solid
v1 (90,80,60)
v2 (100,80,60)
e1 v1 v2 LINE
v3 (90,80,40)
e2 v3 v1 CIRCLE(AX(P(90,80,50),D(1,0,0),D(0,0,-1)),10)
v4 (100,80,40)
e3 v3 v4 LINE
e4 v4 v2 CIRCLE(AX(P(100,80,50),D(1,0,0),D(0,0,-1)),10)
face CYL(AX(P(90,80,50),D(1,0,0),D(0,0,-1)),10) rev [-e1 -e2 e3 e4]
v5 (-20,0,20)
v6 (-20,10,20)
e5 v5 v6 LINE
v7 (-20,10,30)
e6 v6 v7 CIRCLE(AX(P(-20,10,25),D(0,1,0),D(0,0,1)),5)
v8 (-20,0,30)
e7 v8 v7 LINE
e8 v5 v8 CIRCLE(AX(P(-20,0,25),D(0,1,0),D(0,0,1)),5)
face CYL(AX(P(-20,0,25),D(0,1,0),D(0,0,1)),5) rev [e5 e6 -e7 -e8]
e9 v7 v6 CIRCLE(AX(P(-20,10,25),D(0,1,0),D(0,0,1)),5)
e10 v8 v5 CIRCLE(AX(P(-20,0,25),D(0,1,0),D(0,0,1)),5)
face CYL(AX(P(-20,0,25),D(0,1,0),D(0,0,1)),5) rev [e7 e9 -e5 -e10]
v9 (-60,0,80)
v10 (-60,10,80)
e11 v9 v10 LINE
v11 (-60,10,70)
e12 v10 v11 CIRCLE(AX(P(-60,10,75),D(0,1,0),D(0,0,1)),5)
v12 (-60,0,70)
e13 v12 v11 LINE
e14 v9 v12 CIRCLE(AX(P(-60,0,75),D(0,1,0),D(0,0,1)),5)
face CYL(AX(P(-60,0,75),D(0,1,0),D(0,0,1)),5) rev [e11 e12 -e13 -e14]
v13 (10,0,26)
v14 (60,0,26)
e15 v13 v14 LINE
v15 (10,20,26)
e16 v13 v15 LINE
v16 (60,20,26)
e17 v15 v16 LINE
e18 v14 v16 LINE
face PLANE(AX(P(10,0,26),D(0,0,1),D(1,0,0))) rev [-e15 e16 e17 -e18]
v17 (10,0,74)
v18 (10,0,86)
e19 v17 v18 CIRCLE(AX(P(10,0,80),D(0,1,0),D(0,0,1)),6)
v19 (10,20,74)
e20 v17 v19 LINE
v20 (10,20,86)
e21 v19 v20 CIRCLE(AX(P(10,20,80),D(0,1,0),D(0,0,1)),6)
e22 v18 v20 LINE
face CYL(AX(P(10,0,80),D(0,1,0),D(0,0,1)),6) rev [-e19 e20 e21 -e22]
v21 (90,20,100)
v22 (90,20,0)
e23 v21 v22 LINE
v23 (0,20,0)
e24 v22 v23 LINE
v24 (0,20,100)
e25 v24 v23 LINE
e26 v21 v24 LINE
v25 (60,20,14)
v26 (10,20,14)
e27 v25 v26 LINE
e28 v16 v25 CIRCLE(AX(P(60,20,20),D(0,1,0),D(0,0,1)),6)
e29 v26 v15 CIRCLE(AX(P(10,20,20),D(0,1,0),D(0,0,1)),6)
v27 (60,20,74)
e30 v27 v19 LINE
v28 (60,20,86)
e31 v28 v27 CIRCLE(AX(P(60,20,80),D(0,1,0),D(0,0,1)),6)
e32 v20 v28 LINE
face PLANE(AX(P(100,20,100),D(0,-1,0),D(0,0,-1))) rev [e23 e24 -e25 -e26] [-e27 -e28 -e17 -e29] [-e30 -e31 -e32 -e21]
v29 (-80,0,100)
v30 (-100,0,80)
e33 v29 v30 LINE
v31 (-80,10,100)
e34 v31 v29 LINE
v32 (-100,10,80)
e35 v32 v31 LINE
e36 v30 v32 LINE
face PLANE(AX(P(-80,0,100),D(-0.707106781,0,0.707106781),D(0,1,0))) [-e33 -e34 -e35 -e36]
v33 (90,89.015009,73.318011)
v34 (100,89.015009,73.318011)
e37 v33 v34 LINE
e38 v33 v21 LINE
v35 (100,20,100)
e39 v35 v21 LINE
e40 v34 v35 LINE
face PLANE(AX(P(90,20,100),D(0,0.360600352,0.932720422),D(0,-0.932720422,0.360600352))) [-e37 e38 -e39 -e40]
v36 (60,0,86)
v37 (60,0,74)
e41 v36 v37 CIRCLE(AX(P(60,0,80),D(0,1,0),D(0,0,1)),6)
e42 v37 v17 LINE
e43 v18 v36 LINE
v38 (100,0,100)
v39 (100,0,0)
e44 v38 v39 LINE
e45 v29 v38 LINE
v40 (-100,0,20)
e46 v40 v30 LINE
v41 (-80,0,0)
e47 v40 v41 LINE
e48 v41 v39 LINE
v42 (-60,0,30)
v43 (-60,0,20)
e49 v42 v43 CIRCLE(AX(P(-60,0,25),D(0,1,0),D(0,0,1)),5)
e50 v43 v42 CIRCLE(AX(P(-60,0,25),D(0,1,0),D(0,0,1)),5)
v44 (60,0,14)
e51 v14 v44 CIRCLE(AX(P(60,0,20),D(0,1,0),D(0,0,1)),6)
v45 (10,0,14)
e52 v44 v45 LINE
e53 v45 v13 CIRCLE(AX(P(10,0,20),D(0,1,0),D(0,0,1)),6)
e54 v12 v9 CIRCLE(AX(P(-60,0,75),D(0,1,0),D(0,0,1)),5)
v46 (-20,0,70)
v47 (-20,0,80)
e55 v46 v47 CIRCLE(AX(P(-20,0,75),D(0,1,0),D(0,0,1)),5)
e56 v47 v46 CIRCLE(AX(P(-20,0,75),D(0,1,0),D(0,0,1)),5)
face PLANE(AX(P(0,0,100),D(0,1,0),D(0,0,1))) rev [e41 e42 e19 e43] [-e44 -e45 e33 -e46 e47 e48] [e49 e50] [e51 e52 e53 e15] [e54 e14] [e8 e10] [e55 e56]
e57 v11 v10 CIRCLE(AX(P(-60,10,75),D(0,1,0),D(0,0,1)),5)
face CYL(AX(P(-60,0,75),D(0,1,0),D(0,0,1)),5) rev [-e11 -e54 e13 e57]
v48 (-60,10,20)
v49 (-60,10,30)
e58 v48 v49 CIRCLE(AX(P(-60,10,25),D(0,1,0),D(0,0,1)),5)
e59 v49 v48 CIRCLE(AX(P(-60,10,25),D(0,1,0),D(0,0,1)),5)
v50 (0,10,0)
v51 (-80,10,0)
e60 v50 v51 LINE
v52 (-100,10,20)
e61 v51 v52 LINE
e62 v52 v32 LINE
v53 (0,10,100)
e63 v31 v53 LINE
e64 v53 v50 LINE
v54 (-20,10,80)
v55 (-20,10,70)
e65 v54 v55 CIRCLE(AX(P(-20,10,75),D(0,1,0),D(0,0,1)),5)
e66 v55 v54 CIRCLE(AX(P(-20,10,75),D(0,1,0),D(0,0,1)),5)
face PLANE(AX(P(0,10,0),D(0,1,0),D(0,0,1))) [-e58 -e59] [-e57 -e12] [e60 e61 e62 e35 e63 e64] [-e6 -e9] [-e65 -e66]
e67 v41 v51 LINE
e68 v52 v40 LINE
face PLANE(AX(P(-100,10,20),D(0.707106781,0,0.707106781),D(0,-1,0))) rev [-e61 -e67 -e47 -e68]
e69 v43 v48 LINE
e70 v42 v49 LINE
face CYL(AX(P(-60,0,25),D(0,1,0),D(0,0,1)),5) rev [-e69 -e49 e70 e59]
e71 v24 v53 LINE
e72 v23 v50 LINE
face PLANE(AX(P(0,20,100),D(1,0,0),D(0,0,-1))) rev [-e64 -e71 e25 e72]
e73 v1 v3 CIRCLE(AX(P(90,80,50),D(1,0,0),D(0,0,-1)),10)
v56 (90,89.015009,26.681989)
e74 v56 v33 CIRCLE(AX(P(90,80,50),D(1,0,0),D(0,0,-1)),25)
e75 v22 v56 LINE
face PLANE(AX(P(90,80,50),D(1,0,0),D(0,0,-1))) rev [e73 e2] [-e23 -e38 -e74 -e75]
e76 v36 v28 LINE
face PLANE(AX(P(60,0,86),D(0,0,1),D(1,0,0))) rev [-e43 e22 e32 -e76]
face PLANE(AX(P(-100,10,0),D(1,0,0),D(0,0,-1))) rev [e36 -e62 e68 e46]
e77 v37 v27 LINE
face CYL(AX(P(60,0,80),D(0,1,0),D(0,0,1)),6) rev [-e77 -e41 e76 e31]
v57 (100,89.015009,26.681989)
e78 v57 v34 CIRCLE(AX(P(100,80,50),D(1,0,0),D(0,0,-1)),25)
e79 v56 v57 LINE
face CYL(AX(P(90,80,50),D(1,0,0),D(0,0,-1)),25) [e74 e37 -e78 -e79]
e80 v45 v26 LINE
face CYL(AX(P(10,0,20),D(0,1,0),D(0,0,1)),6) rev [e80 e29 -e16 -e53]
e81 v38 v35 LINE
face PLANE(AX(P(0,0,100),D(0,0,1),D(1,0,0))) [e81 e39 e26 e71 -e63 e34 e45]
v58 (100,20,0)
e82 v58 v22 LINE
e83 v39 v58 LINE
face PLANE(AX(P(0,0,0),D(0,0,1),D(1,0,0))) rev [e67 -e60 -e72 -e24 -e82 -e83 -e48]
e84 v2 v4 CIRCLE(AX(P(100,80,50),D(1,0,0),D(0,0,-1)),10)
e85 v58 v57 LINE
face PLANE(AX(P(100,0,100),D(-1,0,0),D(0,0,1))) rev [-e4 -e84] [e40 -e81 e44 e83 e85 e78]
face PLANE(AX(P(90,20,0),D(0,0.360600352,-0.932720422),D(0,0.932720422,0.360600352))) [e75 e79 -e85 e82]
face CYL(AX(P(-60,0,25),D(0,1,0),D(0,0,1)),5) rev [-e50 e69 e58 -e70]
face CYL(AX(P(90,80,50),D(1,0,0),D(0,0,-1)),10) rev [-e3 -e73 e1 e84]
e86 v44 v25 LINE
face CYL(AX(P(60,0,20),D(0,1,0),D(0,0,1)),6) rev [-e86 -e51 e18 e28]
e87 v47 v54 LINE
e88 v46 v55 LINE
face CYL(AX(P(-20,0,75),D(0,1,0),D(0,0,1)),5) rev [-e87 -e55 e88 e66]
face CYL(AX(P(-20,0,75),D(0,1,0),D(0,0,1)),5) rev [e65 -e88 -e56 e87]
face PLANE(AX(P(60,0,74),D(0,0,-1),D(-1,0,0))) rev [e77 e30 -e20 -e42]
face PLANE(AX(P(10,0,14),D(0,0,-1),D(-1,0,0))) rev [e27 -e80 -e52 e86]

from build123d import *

# Parameters (mm, degrees)
BASE_PLATE_SKETCH_W             = 100
BASE_PLATE_SKETCH_H             = 20
BASE_PLATE_DEPTH                = 100
MOUNTING_FLANGE_SKETCH_W        = 100
MOUNTING_FLANGE_SKETCH_H        = 100
MOUNTING_FLANGE_DEPTH           = 10
FLANGE_CORNER_CHAMFER_20MM_SIZE = 20
LUG_PROFILE_SKETCH_R            = 10
UPRIGHT_LUG_DEPTH               = 10
ADJUSTMENT_SLOTS_2X_DEPTH       = 166
MOUNTING_HOLES_SKETCH_R         = 5
FLANGE_MOUNTING_HOLES_DEPTH     = 10


with BuildPart() as part:
    # Base Plate Sketch → Base Plate (new body)
    with BuildSketch(Plane.XY):
        with Locations((50, 10)):
            Rectangle(BASE_PLATE_SKETCH_W, BASE_PLATE_SKETCH_H)
    extrude(amount=BASE_PLATE_DEPTH)

    # Mounting Flange Sketch → Mounting Flange (add)
    with BuildSketch(Plane(origin=(0, 0, 0), x_dir=(1, 0, 0), z_dir=(0, 1, 0))):
        with Locations((-50, -50)):
            Rectangle(MOUNTING_FLANGE_SKETCH_W, MOUNTING_FLANGE_SKETCH_H)
    extrude(amount=MOUNTING_FLANGE_DEPTH)

    # Flange Corner Chamfer 20mm
    flange_corner_chamfer_20mm_edges = [part.edges().sort_by_distance(p)[0] for p in [
        (-100, 5, 0),
        (-100, 5, 100),
    ]]
    chamfer(flange_corner_chamfer_20mm_edges, length=FLANGE_CORNER_CHAMFER_20MM_SIZE)

    # Lug Profile Sketch → Upright Lug (add)
    with BuildSketch(Plane(origin=(100, 0, 0), x_dir=(0, 0, -1), z_dir=(1, 0, 0))):
        with BuildLine():
            Line((-100, 20), (-73.318010558, 89.015008798))
            ThreePointArc((-73.318010558, 89.015008798), (-50, 105), (-26.681989442, 89.015008798))
            Line((-26.681989442, 89.015008798), (0, 20))
            Line((0, 20), (-100, 20))
        make_face()
        with Locations((-50, 80)):
            Circle(LUG_PROFILE_SKETCH_R, mode=Mode.SUBTRACT)
    extrude(amount=-UPRIGHT_LUG_DEPTH)

    # Adjustment Slots Sketch → Adjustment Slots 2x (cut, through all)
    with BuildSketch(Plane(origin=(0, 20, 0), x_dir=(1, 0, 0), z_dir=(0, 1, 0))):
        with BuildLine():
            Line((10, -14), (60, -14))
            ThreePointArc((60, -14), (66, -20), (60, -26))
            Line((60, -26), (10, -26))
            ThreePointArc((10, -26), (4, -20), (10, -14))
        make_face()
        with BuildLine():
            Line((60, -86), (10, -86))
            ThreePointArc((10, -86), (4, -80), (10, -74))
            Line((10, -74), (60, -74))
            ThreePointArc((60, -74), (66, -80), (60, -86))
        make_face()
    extrude(amount=-ADJUSTMENT_SLOTS_2X_DEPTH, mode=Mode.SUBTRACT)

    # Mounting Holes Sketch → Flange Mounting Holes (cut)
    with BuildSketch(Plane(origin=(0, 10, 0), x_dir=(1, 0, 0), z_dir=(0, 1, 0))):
        with Locations(Location((-20, -25, 0), (0, 0, 270))):
            Circle(MOUNTING_HOLES_SKETCH_R)
        with Locations(Location((-60, -25, 0), (0, 0, 270))):
            Circle(MOUNTING_HOLES_SKETCH_R)
        with Locations(Location((-20, -75, 0), (0, 0, 270))):
            Circle(MOUNTING_HOLES_SKETCH_R)
        with Locations(Location((-60, -75, 0), (0, 0, 270))):
            Circle(MOUNTING_HOLES_SKETCH_R)
    extrude(amount=-FLANGE_MOUNTING_HOLES_DEPTH, mode=Mode.SUBTRACT)


solid = part.part
